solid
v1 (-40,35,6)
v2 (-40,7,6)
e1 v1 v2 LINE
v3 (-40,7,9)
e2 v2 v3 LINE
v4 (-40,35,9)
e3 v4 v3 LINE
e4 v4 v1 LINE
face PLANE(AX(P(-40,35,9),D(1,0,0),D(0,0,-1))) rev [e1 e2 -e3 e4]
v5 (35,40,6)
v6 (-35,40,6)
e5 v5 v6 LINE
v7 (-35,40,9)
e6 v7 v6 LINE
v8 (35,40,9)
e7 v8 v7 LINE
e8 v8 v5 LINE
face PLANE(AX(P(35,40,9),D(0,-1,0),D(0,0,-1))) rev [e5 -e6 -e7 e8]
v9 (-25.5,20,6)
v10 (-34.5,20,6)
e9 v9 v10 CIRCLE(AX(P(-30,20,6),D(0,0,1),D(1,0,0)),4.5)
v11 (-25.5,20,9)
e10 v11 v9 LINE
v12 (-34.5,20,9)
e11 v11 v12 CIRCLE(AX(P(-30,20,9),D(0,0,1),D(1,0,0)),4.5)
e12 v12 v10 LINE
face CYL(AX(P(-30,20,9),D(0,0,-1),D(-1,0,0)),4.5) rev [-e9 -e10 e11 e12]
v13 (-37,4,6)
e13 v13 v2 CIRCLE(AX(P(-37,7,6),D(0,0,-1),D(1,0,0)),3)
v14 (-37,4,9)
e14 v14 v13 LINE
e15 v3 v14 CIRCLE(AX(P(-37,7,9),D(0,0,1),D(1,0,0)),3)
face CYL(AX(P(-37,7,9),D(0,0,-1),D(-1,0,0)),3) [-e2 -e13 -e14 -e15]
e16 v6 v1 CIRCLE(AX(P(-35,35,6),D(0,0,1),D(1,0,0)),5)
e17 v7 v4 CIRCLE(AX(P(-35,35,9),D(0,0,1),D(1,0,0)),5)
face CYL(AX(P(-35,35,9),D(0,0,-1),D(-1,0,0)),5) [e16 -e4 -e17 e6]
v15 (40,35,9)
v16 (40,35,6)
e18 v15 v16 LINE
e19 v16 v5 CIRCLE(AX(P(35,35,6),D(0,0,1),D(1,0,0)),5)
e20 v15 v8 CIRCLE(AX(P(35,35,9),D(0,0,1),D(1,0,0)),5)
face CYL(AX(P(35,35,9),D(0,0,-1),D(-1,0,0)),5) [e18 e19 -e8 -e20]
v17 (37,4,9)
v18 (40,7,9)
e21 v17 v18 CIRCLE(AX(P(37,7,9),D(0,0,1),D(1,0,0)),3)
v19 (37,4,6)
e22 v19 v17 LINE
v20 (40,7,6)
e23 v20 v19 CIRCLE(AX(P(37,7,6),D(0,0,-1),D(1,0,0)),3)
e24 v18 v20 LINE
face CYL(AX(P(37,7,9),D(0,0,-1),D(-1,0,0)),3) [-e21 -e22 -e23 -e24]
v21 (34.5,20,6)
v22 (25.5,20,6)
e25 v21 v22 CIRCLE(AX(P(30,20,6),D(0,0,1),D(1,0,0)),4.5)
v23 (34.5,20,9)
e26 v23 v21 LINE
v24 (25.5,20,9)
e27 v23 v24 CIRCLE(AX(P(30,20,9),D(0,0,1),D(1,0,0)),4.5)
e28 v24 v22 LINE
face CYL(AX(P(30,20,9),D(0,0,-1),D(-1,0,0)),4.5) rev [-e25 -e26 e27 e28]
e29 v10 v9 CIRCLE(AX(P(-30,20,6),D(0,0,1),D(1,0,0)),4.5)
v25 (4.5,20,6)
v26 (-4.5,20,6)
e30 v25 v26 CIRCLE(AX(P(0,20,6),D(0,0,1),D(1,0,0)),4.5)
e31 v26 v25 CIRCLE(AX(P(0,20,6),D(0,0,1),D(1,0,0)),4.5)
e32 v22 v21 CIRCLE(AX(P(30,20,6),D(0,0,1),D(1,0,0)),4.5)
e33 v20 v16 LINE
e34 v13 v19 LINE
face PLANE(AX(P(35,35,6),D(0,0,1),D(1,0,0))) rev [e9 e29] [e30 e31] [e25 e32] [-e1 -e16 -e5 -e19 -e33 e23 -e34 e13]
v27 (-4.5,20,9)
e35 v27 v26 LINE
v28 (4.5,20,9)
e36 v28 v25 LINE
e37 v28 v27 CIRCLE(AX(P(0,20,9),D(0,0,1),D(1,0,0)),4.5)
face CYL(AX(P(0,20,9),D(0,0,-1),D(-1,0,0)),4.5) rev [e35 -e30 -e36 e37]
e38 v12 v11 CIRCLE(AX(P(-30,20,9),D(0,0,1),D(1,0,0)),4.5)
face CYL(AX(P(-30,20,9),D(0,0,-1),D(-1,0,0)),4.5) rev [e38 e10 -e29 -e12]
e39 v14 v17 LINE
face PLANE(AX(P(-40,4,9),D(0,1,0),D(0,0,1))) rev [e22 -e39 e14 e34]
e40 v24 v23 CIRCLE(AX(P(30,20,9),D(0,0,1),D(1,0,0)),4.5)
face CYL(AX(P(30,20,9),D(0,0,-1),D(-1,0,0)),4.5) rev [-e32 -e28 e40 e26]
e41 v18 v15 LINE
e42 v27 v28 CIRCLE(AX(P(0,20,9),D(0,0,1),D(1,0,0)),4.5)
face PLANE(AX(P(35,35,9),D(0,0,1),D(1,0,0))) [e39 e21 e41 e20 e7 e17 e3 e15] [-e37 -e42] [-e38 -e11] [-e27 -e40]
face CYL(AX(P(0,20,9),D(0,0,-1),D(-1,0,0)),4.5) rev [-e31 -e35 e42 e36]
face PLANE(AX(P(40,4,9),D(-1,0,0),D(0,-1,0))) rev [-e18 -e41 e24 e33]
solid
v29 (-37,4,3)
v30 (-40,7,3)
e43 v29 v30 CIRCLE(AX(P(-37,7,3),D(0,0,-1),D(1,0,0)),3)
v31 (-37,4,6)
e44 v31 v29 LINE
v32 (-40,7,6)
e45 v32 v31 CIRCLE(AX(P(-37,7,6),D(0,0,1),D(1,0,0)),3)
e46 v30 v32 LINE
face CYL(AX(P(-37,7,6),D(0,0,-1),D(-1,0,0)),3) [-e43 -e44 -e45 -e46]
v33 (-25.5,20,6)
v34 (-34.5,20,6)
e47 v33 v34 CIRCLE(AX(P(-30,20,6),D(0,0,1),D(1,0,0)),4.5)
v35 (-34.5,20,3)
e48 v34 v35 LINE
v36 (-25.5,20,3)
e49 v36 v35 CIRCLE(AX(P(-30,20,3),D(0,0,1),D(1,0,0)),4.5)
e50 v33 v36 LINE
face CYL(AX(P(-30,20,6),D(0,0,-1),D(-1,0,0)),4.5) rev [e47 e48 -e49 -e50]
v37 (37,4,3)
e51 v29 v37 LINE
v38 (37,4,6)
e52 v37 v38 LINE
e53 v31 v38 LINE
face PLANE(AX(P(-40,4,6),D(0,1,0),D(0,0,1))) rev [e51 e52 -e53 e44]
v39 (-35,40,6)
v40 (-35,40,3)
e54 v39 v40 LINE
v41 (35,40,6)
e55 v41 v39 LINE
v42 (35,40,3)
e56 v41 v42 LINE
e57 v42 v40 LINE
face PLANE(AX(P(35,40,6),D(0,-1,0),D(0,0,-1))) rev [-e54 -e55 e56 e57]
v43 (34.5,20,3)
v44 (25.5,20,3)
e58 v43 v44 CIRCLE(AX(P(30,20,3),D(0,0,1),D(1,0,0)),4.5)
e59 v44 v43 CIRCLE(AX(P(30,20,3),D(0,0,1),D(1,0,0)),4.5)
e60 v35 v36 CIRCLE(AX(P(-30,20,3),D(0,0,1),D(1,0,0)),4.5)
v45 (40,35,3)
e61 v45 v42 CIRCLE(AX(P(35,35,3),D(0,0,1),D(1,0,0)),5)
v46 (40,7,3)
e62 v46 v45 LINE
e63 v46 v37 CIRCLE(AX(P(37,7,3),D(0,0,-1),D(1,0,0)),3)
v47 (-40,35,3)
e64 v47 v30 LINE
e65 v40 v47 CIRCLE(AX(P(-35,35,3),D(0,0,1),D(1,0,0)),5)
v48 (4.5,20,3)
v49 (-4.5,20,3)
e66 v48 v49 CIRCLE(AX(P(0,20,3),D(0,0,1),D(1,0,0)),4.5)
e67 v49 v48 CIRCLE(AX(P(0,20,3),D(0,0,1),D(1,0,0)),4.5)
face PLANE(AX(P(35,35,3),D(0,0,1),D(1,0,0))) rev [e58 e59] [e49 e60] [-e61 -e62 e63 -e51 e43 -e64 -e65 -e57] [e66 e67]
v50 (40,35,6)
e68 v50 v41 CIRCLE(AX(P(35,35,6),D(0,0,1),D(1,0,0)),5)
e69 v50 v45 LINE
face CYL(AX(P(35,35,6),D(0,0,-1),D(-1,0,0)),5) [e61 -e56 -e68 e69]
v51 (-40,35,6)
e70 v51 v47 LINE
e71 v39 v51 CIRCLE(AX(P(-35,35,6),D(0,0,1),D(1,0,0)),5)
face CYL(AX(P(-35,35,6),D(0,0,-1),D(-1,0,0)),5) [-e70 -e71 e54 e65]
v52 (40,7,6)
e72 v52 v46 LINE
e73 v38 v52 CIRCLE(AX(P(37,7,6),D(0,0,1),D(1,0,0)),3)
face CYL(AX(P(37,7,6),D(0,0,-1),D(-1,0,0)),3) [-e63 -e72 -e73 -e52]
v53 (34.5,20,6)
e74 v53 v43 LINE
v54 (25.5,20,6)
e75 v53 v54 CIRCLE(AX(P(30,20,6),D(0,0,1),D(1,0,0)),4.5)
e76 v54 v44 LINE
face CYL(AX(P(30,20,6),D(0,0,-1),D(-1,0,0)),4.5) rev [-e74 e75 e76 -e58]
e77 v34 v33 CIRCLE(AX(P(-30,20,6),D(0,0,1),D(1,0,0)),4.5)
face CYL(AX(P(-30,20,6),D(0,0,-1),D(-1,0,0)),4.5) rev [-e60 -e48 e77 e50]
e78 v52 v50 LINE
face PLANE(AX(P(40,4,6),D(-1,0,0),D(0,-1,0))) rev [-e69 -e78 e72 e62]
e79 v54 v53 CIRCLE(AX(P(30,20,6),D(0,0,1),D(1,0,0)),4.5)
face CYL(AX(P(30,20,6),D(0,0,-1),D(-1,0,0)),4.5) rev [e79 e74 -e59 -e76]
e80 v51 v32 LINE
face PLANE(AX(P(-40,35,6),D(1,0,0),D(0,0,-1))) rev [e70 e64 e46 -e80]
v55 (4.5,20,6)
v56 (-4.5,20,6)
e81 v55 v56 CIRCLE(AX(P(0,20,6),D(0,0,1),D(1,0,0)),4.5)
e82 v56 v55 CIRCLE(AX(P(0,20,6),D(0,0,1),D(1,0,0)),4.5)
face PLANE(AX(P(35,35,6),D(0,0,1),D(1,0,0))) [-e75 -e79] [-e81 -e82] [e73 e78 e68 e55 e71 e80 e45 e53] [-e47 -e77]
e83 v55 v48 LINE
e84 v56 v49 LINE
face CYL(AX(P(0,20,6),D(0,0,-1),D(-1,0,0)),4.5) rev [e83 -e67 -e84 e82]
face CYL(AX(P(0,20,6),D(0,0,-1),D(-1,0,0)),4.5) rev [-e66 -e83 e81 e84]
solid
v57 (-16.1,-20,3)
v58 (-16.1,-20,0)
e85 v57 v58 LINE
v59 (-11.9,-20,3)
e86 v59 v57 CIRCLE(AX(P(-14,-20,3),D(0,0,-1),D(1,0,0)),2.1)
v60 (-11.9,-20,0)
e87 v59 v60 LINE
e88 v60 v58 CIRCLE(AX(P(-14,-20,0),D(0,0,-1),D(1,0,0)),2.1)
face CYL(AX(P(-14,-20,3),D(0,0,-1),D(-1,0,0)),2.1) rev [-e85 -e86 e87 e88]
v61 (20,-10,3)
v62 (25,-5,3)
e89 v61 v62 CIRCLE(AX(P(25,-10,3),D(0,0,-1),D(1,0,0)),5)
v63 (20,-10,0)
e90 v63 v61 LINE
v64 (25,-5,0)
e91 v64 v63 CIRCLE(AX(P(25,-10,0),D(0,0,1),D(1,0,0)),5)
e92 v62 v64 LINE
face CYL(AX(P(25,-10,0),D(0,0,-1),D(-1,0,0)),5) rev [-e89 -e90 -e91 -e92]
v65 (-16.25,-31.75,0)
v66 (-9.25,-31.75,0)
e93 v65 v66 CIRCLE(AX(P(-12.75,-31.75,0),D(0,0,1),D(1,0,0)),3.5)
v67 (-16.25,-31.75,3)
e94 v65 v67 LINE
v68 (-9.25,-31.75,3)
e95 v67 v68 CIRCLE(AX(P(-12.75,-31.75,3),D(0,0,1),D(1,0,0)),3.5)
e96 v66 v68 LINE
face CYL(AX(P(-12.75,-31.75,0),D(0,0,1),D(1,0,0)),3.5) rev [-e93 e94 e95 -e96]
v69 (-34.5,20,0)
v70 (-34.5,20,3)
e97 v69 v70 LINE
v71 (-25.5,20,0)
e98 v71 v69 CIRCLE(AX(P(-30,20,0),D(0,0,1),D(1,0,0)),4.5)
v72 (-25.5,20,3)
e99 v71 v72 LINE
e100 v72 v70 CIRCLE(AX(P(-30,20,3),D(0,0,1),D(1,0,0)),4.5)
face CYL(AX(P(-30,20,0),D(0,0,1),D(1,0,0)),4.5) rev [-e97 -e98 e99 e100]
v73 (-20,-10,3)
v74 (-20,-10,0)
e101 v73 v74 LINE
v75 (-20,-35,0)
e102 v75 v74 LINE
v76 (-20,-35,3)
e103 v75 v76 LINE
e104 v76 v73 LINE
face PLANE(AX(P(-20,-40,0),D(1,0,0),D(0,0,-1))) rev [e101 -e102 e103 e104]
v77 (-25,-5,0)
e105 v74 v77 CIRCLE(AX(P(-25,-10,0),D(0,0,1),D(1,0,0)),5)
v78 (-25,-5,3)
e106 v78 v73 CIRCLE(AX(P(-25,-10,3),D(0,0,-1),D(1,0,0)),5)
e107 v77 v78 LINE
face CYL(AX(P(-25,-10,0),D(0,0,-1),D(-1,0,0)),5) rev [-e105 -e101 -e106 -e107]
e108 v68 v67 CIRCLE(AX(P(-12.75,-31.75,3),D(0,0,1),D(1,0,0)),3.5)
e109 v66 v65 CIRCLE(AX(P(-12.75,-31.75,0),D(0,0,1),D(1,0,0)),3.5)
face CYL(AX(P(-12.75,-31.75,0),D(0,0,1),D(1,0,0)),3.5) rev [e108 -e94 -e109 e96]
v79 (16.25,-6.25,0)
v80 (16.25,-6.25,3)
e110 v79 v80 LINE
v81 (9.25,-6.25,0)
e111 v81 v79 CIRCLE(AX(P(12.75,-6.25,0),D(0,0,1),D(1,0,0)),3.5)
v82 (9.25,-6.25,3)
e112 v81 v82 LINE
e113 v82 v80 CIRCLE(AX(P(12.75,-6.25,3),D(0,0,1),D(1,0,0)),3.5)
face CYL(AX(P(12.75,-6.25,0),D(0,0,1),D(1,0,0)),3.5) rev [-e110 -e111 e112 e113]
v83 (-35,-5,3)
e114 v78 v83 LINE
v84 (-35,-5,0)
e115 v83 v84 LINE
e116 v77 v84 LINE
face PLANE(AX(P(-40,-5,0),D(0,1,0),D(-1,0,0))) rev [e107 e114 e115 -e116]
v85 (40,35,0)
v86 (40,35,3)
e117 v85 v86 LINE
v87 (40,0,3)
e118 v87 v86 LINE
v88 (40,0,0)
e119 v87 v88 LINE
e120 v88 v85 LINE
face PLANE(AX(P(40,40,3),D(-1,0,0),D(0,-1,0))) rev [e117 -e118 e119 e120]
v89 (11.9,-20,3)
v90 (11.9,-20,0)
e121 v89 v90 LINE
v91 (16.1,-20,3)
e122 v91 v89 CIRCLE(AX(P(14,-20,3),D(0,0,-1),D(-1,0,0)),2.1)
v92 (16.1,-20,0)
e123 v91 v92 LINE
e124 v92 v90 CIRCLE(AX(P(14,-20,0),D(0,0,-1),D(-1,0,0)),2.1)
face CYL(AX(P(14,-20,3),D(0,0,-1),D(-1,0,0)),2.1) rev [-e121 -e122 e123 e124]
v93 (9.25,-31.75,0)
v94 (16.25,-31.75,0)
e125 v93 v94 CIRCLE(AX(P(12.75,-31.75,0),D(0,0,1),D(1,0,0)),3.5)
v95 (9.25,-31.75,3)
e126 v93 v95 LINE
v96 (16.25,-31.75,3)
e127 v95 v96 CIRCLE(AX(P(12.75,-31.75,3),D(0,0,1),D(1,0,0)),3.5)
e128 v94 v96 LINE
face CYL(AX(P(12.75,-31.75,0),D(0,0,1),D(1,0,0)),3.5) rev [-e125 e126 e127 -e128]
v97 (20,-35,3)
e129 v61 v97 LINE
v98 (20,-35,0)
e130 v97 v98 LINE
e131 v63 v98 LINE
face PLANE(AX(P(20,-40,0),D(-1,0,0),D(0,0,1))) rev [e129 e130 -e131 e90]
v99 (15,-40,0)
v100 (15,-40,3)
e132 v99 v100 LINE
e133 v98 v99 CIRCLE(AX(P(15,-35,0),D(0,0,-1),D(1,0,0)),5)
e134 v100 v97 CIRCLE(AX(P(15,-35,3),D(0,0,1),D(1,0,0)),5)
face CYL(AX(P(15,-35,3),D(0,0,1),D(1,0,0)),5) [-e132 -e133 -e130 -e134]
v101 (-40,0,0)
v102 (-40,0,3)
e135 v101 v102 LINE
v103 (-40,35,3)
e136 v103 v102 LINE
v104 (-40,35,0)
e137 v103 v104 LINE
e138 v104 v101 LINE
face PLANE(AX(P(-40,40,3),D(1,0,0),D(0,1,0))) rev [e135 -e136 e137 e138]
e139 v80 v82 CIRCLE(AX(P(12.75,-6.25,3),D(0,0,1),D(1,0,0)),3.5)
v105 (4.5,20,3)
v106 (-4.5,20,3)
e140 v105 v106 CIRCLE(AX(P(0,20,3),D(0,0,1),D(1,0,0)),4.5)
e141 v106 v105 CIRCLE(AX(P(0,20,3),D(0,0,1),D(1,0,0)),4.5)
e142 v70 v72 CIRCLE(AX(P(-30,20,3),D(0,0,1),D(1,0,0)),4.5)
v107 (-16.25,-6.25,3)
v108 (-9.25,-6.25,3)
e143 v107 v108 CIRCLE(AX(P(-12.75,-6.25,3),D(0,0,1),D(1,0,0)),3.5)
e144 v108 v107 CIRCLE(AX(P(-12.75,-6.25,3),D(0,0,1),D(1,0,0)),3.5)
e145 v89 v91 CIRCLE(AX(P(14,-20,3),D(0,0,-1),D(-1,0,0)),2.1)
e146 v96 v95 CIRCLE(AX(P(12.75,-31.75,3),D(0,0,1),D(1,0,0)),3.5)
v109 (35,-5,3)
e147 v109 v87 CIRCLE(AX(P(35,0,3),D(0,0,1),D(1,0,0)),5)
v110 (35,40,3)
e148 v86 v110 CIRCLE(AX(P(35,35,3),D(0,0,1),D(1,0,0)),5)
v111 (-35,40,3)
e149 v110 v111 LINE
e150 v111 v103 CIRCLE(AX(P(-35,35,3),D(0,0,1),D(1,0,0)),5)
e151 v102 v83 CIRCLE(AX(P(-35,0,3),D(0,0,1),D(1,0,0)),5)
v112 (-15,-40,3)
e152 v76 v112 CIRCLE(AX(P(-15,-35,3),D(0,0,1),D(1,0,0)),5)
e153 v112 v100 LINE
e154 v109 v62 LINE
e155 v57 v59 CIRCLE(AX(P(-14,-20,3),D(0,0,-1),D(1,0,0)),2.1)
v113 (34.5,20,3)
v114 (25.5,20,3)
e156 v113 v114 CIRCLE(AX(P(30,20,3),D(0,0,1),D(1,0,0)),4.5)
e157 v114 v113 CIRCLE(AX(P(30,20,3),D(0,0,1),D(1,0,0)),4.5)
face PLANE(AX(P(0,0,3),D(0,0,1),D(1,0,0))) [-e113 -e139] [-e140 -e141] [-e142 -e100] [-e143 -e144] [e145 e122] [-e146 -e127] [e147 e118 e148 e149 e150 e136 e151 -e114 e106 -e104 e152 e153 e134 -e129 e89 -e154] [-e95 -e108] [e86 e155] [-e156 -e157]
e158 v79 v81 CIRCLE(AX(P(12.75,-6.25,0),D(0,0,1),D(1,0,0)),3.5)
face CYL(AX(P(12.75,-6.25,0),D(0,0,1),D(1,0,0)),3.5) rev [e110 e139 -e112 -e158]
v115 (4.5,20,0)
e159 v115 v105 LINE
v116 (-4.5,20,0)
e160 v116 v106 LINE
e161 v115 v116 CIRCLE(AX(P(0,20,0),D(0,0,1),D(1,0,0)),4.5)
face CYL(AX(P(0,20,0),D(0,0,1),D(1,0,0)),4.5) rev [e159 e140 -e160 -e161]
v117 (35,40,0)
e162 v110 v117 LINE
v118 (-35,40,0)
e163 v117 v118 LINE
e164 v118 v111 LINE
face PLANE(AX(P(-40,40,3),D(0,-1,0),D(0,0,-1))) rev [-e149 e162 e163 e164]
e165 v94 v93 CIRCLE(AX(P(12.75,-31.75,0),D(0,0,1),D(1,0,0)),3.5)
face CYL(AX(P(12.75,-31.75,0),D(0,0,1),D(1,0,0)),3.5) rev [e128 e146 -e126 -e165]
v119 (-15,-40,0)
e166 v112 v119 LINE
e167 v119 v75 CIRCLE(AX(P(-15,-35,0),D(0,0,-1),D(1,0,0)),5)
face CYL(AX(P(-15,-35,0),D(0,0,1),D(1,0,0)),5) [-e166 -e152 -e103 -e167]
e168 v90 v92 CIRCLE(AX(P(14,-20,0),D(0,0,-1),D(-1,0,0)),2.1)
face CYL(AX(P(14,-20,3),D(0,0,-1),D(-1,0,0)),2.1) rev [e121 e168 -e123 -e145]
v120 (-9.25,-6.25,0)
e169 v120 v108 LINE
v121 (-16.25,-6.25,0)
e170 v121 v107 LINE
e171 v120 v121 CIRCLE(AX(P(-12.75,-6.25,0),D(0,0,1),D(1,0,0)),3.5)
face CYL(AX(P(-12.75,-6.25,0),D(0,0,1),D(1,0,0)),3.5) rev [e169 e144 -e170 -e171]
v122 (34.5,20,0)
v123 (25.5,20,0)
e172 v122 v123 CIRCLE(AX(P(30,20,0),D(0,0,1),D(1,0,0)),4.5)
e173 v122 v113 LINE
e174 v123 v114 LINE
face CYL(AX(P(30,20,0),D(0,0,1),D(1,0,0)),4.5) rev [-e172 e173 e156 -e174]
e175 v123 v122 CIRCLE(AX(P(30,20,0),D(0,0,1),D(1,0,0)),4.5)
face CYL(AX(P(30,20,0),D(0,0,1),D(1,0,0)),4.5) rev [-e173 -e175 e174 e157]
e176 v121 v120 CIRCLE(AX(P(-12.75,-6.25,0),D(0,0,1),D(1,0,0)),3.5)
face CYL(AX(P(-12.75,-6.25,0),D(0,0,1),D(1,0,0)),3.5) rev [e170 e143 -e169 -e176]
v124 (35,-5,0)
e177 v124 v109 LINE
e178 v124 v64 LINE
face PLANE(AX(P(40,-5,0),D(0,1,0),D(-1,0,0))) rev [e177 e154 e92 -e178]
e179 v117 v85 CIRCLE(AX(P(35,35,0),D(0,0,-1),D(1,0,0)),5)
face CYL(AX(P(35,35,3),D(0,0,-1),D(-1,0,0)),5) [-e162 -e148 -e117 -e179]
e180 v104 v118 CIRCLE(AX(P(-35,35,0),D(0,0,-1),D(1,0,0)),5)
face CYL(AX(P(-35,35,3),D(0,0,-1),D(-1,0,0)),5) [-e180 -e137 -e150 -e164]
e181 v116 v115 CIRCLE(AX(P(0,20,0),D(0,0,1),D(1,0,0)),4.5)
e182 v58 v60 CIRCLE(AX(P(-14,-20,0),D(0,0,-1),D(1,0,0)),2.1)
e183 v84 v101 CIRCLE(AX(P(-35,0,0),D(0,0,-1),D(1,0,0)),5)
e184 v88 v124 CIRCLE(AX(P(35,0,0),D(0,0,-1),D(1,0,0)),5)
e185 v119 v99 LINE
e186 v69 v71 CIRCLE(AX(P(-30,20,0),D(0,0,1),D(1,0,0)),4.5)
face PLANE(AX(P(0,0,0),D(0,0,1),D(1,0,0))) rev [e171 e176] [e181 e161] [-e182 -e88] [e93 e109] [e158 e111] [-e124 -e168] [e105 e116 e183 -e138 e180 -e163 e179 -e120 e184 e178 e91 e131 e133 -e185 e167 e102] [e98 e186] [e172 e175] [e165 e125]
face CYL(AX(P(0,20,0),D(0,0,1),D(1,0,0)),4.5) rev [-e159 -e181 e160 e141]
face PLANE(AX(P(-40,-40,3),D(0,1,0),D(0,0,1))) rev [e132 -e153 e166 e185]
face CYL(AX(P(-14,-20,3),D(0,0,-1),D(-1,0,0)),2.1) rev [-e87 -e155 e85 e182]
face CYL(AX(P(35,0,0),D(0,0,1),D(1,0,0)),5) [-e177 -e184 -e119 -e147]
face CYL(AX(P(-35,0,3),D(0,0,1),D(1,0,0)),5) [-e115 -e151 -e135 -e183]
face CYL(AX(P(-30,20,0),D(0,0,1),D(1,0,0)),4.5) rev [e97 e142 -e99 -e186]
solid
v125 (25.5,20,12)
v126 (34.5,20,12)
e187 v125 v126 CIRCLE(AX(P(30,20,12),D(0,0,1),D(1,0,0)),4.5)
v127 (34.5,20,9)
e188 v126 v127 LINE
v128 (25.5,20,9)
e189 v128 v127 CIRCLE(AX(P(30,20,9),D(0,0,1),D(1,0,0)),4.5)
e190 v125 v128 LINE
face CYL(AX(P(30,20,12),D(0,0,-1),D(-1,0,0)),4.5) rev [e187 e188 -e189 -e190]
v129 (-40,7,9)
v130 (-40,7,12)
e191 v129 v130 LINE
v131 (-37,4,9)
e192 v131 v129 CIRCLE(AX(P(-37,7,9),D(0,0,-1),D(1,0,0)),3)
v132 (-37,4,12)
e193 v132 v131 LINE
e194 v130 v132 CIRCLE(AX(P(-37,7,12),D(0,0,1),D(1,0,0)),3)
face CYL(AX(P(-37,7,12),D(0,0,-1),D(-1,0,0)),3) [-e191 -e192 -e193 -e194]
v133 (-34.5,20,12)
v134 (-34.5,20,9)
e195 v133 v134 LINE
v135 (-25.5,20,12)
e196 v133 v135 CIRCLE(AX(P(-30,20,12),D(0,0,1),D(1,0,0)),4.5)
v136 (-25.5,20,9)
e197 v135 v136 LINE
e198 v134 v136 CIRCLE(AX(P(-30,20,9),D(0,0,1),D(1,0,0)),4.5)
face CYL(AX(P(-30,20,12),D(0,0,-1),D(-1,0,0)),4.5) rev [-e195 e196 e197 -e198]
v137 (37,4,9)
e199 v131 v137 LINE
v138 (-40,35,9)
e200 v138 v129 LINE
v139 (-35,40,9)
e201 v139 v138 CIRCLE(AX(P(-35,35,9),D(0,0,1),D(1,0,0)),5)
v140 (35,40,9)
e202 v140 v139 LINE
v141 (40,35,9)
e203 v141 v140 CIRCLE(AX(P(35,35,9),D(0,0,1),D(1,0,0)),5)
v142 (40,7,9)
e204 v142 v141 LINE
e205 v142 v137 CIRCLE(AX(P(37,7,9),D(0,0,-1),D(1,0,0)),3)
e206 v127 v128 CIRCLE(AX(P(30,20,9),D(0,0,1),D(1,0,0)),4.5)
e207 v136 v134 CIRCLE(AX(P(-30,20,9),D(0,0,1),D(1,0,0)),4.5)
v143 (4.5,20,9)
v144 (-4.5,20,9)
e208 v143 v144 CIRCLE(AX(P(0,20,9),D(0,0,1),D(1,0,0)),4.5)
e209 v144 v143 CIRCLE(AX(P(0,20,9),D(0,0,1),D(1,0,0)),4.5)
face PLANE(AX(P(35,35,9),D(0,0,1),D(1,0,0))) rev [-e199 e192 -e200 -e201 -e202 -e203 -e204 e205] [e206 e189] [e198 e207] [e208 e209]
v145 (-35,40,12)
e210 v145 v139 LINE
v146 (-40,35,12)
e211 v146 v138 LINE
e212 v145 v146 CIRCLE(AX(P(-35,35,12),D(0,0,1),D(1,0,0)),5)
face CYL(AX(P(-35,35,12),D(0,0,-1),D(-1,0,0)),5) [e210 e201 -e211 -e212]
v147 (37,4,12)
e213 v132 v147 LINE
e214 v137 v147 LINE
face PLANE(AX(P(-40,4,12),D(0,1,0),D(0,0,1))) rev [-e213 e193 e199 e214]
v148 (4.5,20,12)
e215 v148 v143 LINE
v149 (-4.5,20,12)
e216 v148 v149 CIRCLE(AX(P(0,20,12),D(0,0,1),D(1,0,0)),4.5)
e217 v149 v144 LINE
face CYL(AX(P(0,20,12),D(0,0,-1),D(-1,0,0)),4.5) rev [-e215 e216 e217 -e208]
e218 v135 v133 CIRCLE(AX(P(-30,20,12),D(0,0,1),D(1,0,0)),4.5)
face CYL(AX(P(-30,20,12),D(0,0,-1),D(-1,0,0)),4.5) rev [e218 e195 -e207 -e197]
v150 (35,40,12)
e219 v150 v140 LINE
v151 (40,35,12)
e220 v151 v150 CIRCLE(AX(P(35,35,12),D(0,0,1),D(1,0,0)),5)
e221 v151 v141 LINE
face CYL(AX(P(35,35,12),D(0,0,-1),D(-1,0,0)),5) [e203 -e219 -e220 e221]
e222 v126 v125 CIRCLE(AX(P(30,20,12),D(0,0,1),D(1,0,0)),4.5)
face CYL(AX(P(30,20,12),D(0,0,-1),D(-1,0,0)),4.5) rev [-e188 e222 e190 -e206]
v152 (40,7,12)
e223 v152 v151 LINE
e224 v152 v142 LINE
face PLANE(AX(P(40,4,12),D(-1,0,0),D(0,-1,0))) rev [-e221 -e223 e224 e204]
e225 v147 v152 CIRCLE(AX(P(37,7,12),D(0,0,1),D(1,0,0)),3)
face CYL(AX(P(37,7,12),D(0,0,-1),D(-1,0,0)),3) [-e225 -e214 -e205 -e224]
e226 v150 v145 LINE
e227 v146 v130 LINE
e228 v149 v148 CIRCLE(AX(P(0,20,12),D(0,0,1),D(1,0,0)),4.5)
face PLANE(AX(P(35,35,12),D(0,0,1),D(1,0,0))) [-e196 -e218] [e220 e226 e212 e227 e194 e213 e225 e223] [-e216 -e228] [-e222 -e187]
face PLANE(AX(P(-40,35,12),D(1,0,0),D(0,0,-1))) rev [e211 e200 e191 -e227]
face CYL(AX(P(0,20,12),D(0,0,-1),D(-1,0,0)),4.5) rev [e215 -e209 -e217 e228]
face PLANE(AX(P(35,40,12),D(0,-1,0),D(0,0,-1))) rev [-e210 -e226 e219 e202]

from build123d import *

# Parameters (mm, degrees)
SKETCH_1_W             = 80
SKETCH_1_H             = 80
EXTRUDE_1_DEPTH        = 3
SKETCH_5_W             = 20
SKETCH_5_H             = 35
CUT_EXTRUDE_3_DEPTH    = 3
FILLET_1_R             = 5
SKETCH_2_R             = 4.5
CUT_EXTRUDE_1_DEPTH    = 3
SKETCH_3_R             = 3.5
CUT_EXTRUDE_2_DEPTH    = 3
SKETCH_4_R             = 4.5
EXTRUDE_2_DEPTH        = 3
FILLET_2_R             = 3
PATTERN_LINEAR_1_COUNT = 3
PATTERN_LINEAR_1_PITCH = 3
SKETCH_6_R             = 2.1
CUT_EXTRUDE_4_DEPTH    = 3
FILLET_3_R             = 5


with BuildPart() as part:
    # 草图1 → 凸台-拉伸1 (new body)
    with BuildSketch(Plane.XY):
        Rectangle(SKETCH_1_W, SKETCH_1_H)
    extrude(amount=EXTRUDE_1_DEPTH)

    # 草图5 → 切除-拉伸3 (cut)
    with BuildSketch(Plane.XY.offset(3)):
        with Locations((30, -22.5)):
            Rectangle(SKETCH_5_W, SKETCH_5_H)
        with Locations((-30, -22.5)):
            Rectangle(SKETCH_5_W, SKETCH_5_H)
    extrude(amount=-CUT_EXTRUDE_3_DEPTH, mode=Mode.SUBTRACT)

    # 圆角1
    fillet_1_edges = [part.edges().sort_by_distance(p)[0] for p in [
        (40, -5, 1.5),
        (20, -40, 1.5),
        (-20, -40, 1.5),
        (-40, -5, 1.5),
        (-40, 40, 1.5),
        (40, 40, 1.5),
    ]]
    fillet(fillet_1_edges, radius=FILLET_1_R)

    # 草图2 → 切除-拉伸1 (cut)
    with BuildSketch(Plane.XY.offset(3)):
        with Locations((-30, 20)):
            Circle(SKETCH_2_R)
        with Locations((0, 20)):
            Circle(SKETCH_2_R)
        with Locations((30, 20)):
            Circle(SKETCH_2_R)
    extrude(amount=-CUT_EXTRUDE_1_DEPTH, mode=Mode.SUBTRACT)

    # 草图3 → 切除-拉伸2 (cut)
    with BuildSketch(Plane.XY.offset(3)):
        with Locations((12.75, -6.25)):
            Circle(SKETCH_3_R)
        with Locations((12.75, -31.75)):
            Circle(SKETCH_3_R)
        with Locations((-12.75, -31.75)):
            Circle(SKETCH_3_R)
        with Locations((-12.75, -6.25)):
            Circle(SKETCH_3_R)
    extrude(amount=-CUT_EXTRUDE_2_DEPTH, mode=Mode.SUBTRACT)

    # 草图6 → 切除-拉伸4 (cut)
    with BuildSketch(Plane(origin=(0, 0, 0), x_dir=(-1, 0, 0), z_dir=(0, 0, -1))):
        with Locations((-14, -20)):
            Circle(SKETCH_6_R)
        with Locations(Location((14, -20, 0), (0, 0, 180))):
            Circle(SKETCH_6_R)
    extrude(amount=-CUT_EXTRUDE_4_DEPTH, mode=Mode.SUBTRACT)

    # 圆角3
    fillet_3_edges = [part.edges().sort_by_distance(p)[0] for p in [
        (20, -5, 1.5),
        (-20, -5, 1.5),
    ]]
    fillet(fillet_3_edges, radius=FILLET_3_R)


with BuildPart() as body_2:
    # 草图4 → 凸台-拉伸2 (new body)
    with BuildSketch(Plane.XY.offset(3)):
        with BuildLine():
            Line((-40, 4), (40, 4))
            Line((40, 4), (40, 35))
            ThreePointArc((40, 35), (38.535533906, 38.535533906), (35, 40))
            Line((35, 40), (-35, 40))
            ThreePointArc((-35, 40), (-38.535533906, 38.535533906), (-40, 35))
            Line((-40, 35), (-40, 4))
        make_face()
        with Locations((30, 20)):
            Circle(SKETCH_4_R, mode=Mode.SUBTRACT)
        with Locations((-30, 20)):
            Circle(SKETCH_4_R, mode=Mode.SUBTRACT)
        with Locations((0, 20)):
            Circle(SKETCH_4_R, mode=Mode.SUBTRACT)
    extrude(amount=EXTRUDE_2_DEPTH)

    # 圆角2
    fillet_2_edges = [body_2.edges().sort_by_distance(p)[0] for p in [
        (40, 4, 4.5),
        (-40, 4, 4.5),
    ]]
    fillet(fillet_2_edges, radius=FILLET_2_R)


with BuildPart() as pattern_linear_1_1:
    # 阵列(线性)1: pattern copy
    add(body_2.part.moved(Location(Vector(0, 0, 1) * (1 * PATTERN_LINEAR_1_PITCH))))


with BuildPart() as pattern_linear_1_2:
    # 阵列(线性)1: pattern copy
    add(body_2.part.moved(Location(Vector(0, 0, 1) * (2 * PATTERN_LINEAR_1_PITCH))))


solid = Compound([part.part, body_2.part, pattern_linear_1_1.part, pattern_linear_1_2.part])
